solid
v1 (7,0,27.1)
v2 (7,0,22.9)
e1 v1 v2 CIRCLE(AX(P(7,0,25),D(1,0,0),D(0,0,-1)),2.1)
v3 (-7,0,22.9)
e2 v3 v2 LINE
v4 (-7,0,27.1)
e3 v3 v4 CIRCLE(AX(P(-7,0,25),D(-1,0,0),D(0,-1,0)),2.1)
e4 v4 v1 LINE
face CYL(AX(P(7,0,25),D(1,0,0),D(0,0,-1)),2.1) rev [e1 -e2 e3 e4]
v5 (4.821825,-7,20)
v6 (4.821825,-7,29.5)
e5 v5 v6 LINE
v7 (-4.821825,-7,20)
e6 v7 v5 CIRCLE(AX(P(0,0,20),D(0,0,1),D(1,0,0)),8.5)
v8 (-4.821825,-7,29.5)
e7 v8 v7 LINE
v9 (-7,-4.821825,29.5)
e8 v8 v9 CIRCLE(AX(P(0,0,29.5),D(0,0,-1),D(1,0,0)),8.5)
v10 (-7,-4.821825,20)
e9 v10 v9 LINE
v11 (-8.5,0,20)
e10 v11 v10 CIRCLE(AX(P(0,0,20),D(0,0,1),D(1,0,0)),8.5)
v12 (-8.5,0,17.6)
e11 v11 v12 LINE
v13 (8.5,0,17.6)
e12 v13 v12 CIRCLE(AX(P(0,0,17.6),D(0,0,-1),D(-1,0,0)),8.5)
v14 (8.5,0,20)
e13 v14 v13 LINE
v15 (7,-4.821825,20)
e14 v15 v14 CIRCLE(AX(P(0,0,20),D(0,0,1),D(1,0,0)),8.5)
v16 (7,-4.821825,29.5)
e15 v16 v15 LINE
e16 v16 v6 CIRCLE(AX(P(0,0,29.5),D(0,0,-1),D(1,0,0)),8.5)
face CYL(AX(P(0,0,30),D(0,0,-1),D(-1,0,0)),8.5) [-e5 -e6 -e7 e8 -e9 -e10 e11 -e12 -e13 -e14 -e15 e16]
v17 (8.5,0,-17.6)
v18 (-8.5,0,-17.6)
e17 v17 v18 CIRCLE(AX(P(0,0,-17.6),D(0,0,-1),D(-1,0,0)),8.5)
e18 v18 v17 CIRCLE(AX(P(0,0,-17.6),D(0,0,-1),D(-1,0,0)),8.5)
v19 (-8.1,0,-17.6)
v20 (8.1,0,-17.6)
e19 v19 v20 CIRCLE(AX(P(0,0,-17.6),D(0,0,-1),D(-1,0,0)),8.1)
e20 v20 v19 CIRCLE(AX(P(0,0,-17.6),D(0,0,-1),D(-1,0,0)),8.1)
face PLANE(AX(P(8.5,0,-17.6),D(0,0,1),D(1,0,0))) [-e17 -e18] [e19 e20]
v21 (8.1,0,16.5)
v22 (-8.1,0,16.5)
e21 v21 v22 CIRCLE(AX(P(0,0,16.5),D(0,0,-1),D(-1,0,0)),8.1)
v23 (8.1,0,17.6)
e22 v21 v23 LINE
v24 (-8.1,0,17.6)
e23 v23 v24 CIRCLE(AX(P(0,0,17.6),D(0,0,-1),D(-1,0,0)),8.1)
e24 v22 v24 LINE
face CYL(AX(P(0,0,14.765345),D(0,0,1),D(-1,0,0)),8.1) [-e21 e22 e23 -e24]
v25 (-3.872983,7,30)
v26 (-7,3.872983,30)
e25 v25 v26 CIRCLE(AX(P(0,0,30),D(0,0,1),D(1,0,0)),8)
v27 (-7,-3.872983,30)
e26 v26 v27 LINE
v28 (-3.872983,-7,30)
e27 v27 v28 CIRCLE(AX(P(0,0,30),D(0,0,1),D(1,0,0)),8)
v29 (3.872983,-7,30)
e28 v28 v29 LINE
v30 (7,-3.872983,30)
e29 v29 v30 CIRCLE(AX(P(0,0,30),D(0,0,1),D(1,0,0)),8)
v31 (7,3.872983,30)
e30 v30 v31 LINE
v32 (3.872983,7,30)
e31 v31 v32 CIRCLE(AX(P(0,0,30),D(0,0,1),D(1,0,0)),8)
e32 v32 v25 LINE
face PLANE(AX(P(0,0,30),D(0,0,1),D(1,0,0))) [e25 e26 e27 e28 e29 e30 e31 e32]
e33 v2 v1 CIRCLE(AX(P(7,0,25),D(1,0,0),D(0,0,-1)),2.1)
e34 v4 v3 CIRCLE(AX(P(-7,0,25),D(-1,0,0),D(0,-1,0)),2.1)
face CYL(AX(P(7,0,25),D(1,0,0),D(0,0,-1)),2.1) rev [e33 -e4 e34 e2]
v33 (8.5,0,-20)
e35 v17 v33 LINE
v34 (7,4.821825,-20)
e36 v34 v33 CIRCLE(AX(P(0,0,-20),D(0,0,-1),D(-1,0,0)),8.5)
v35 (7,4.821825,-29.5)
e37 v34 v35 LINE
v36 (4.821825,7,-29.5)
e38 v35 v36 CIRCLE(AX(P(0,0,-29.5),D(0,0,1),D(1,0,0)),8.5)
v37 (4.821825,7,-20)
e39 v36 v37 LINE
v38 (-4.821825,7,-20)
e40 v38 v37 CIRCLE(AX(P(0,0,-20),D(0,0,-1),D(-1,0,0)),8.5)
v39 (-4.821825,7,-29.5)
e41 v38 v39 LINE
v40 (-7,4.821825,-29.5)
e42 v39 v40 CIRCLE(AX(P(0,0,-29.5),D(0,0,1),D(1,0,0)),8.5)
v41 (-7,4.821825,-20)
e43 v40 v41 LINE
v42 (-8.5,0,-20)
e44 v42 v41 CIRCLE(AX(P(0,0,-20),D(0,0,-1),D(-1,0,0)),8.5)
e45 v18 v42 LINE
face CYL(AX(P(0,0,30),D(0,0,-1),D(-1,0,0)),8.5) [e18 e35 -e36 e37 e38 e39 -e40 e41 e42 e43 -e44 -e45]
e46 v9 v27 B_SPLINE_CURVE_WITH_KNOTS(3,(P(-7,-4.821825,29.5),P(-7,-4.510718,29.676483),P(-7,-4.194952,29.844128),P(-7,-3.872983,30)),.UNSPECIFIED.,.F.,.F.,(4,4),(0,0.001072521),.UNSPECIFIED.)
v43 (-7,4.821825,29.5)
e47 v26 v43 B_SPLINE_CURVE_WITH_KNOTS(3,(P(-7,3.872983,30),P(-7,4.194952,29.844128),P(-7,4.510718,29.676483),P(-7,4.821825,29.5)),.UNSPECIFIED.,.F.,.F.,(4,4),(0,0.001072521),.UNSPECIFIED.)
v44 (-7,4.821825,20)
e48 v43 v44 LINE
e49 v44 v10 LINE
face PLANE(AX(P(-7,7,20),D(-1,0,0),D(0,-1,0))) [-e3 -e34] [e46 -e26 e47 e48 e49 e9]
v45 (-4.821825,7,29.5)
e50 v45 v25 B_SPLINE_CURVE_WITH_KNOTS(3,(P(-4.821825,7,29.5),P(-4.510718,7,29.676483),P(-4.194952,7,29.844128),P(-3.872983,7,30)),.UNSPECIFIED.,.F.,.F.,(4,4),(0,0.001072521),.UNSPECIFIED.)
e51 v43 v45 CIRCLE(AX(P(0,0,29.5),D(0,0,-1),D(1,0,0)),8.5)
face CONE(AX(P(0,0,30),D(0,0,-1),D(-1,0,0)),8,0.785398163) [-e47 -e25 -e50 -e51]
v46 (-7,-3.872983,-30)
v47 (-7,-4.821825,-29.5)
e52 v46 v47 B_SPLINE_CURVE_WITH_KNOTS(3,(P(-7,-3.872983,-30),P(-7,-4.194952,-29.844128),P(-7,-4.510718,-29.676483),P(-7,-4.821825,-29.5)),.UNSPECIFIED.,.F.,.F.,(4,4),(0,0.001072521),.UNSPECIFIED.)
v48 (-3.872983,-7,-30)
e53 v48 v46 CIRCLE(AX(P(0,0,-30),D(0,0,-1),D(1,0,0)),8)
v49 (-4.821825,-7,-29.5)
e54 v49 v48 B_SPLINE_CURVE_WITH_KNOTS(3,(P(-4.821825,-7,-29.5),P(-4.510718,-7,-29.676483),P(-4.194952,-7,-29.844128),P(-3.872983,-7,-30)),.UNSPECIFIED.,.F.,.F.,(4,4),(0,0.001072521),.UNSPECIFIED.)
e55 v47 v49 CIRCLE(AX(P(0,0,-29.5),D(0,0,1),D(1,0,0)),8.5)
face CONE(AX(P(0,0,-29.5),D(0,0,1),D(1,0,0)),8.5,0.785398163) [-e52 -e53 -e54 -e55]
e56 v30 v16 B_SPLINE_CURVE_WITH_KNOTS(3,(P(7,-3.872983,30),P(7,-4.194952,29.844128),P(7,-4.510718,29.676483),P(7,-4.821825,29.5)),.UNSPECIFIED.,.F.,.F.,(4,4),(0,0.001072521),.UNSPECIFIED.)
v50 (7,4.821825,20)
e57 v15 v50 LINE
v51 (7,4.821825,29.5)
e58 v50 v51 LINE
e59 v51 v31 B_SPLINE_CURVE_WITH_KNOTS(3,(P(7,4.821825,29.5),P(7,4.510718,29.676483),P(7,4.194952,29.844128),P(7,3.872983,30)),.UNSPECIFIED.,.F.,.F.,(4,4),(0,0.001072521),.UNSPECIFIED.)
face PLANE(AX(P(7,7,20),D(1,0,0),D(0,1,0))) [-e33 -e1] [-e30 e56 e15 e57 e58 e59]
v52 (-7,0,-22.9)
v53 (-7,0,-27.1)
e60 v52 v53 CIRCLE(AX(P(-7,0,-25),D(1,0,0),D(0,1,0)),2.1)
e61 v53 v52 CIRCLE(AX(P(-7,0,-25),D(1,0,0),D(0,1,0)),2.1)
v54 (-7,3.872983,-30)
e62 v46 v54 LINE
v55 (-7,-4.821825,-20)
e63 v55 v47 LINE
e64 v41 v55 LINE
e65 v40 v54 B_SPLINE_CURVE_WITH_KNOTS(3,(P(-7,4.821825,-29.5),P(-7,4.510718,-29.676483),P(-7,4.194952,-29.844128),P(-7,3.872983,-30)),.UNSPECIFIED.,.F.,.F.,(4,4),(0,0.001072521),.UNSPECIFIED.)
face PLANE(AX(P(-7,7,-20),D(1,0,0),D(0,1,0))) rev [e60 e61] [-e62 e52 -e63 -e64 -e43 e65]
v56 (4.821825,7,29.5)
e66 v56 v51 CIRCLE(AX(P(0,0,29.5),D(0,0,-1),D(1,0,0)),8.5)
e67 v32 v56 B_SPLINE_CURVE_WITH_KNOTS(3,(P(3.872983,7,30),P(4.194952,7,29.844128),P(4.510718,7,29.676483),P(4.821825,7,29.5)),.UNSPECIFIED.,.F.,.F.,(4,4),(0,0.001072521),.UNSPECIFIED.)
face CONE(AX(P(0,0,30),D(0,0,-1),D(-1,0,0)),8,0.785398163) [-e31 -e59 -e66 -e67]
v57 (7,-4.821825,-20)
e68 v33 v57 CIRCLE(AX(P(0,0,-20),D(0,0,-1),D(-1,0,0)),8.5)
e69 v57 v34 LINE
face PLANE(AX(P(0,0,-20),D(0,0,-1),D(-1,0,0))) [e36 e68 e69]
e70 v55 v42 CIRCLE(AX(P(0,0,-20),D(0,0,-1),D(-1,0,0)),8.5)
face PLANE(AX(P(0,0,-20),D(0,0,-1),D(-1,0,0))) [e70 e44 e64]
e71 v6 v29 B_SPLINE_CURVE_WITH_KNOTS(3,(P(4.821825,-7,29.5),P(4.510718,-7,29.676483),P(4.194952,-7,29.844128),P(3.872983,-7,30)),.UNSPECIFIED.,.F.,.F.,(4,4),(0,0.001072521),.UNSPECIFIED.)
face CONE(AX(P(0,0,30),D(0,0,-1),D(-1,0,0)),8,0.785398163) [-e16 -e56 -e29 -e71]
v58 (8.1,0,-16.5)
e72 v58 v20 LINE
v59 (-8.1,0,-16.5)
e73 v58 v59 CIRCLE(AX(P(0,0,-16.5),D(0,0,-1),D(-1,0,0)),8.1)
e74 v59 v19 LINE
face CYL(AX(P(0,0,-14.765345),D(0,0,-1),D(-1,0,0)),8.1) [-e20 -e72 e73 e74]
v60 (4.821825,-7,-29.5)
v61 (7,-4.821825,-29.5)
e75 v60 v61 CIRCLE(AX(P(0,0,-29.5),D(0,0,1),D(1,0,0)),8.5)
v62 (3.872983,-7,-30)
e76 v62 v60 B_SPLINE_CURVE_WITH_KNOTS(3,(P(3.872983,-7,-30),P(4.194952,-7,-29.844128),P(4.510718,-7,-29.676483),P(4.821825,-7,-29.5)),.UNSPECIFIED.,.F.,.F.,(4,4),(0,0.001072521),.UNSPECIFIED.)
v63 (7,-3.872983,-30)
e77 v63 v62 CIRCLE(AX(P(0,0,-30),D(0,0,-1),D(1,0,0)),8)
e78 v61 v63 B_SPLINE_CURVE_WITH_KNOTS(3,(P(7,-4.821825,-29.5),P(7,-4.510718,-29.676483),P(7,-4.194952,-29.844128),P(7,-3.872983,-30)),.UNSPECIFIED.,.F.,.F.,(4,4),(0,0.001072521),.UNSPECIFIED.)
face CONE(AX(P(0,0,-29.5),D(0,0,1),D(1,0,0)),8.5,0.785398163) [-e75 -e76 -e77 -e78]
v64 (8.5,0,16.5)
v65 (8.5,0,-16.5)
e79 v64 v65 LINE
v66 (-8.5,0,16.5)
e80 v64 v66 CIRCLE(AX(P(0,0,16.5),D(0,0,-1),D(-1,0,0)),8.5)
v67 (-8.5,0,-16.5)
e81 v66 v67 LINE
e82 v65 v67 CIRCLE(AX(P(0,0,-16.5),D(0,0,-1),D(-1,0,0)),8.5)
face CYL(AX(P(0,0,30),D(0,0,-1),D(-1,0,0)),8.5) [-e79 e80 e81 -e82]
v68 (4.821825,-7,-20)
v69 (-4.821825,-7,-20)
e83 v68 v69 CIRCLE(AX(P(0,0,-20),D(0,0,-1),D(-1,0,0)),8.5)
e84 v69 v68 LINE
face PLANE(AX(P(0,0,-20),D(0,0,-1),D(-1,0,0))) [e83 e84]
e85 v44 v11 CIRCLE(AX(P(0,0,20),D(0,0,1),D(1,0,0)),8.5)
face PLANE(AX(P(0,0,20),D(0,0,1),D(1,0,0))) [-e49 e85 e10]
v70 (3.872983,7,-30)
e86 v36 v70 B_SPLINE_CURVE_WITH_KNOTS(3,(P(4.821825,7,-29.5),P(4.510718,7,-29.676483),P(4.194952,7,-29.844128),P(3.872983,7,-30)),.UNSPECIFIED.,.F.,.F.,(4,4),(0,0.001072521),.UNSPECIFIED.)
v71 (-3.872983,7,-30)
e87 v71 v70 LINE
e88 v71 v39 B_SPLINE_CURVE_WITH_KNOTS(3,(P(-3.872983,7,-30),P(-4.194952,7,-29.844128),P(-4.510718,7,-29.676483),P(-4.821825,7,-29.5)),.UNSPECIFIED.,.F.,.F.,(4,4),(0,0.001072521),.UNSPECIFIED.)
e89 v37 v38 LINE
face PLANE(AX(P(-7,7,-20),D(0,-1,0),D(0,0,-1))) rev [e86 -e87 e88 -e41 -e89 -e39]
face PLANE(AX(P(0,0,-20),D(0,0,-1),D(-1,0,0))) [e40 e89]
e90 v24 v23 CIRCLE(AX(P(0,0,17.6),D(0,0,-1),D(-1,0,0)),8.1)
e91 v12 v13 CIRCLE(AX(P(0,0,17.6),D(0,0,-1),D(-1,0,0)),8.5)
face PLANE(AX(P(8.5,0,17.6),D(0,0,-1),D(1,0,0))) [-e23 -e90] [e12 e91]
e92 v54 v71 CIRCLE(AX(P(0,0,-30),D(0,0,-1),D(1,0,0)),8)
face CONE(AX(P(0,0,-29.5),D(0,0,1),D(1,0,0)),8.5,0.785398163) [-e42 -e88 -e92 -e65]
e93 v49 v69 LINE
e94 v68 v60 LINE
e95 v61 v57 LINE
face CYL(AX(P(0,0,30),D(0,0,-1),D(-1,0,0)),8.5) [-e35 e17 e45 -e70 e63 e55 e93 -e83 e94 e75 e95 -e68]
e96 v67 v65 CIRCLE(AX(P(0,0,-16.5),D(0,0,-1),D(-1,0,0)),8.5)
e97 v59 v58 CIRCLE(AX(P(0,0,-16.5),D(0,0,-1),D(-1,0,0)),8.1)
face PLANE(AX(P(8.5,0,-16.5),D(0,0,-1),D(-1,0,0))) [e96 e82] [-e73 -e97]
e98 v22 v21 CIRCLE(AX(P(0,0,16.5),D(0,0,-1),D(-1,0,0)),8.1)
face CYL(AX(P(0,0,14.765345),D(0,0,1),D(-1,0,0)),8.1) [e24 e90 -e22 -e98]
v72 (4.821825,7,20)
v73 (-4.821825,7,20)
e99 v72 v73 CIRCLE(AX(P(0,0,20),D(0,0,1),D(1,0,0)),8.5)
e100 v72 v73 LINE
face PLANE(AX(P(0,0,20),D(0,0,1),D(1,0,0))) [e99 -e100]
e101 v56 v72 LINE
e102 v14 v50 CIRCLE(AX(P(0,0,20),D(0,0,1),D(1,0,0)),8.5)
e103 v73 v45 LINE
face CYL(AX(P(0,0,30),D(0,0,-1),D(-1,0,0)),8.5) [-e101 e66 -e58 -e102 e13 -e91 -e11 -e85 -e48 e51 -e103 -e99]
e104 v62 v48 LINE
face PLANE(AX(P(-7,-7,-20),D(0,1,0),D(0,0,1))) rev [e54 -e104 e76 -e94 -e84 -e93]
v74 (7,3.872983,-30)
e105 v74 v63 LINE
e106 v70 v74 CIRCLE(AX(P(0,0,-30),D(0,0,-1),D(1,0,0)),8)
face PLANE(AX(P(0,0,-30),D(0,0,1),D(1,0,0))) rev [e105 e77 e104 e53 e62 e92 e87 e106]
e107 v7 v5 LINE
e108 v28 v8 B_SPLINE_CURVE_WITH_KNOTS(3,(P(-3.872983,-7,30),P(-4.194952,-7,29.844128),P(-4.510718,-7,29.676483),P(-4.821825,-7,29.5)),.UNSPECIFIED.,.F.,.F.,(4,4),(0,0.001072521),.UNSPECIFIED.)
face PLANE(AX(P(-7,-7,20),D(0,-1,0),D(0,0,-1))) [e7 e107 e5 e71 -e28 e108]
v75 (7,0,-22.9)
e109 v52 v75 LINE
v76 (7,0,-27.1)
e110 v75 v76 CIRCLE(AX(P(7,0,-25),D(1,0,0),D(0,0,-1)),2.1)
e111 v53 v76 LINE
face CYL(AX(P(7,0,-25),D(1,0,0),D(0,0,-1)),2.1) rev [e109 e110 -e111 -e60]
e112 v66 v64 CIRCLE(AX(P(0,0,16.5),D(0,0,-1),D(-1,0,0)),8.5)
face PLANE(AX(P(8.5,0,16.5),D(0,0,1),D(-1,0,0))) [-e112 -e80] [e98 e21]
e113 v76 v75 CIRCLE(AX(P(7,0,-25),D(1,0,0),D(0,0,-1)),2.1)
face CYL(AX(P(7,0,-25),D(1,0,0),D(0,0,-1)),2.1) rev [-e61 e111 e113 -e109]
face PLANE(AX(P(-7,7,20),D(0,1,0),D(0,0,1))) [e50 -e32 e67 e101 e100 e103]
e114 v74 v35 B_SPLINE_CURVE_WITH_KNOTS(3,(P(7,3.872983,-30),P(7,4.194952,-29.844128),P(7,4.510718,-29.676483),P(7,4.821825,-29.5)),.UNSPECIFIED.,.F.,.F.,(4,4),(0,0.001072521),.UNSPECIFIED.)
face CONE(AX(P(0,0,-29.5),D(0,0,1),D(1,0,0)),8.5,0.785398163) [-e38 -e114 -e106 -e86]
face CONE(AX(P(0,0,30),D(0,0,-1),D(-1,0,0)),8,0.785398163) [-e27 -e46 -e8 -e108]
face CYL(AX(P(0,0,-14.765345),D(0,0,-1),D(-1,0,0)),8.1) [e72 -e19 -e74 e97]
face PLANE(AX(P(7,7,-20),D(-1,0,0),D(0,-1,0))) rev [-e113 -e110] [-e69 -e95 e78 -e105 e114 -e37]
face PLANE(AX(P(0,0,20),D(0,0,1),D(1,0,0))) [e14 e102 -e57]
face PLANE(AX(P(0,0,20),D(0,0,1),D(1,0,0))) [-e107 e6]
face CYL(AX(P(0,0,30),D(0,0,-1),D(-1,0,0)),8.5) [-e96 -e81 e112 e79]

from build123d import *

# Parameters (mm, degrees)
SKETCH_1_R           = 8.5
EXTRUDE_1_DEPTH      = 30
SKETCH_4_OUTSIDE_W   = 31.928
SKETCH_4_OUTSIDE_H   = 31.928
SKETCH_4_OUTSIDE_W_2 = 14
SKETCH_4_OUTSIDE_H_2 = 14
CUT_EXTRUDE_1_DEPTH  = 10
HOLE_WIZARD_M5_1_D   = 4.2
CHAMFER_1_SIZE       = 0.5
SKETCH_7_W           = 0.4
SKETCH_7_H           = 1.1


with BuildPart() as part:
    # 草图1 → 凸台-拉伸1 (new, symmetric)
    with BuildSketch(Plane.XY):
        Circle(SKETCH_1_R)
    extrude(amount=EXTRUDE_1_DEPTH, both=True)

    # 草图4 outside → 切除-拉伸1 (cut)
    with BuildSketch(Plane.XY.offset(30)):
        Rectangle(SKETCH_4_OUTSIDE_W, SKETCH_4_OUTSIDE_H)
        Rectangle(SKETCH_4_OUTSIDE_W_2, SKETCH_4_OUTSIDE_H_2, mode=Mode.SUBTRACT)
    cut_extrude_1 = extrude(amount=-CUT_EXTRUDE_1_DEPTH, mode=Mode.SUBTRACT)

    # M5 螺纹孔1 (through all)
    with Locations(Plane(origin=(7, 0, 0), x_dir=(0, 0, -1), z_dir=(1, 0, 0))):
        with Locations((-25, 0)):
            hole_wizard_m5_1 = Hole(HOLE_WIZARD_M5_1_D / 2)

    # 镜向1: 切除-拉伸1, M5 螺纹孔1 across plane
    add(cut_extrude_1.mirror(Plane.XY), mode=Mode.SUBTRACT)
    add(hole_wizard_m5_1.mirror(Plane.XY), mode=Mode.SUBTRACT)

    # 倒角1
    chamfer_1_edges = [part.edges().sort_by_distance(p)[0] for p in [
        (6.01040764, 6.01040764, -30),
        (6.01040764, 6.01040764, 30),
        (-6.01040764, 6.01040764, 30),
        (-6.01040764, 6.01040764, -30),
        (-6.01040764, -6.01040764, -30),
        (6.01040764, -6.01040764, -30),
        (-6.01040764, -6.01040764, 30),
        (6.01040764, -6.01040764, 30),
    ]]
    chamfer(chamfer_1_edges, length=CHAMFER_1_SIZE)

    # 草图7 → 切除-旋转1 (revolve, cut)
    with BuildSketch(Plane(origin=(0, 0, 0), x_dir=(1, 0, 0), z_dir=(0, 1, 0)), mode=Mode.PRIVATE) as cut_revolve_1_sk:
        with Locations((8.3, 17.05)):
            Rectangle(SKETCH_7_W, SKETCH_7_H)
    cut_revolve_1 = revolve(cut_revolve_1_sk.sketch.rotate(Axis((0, 0, -14.7653446), (0, 0, 1)), 180), axis=Axis((0, 0, -14.7653446), (0, 0, 1)), mode=Mode.SUBTRACT)

    # 镜向2: 切除-旋转1 across plane
    add(cut_revolve_1.mirror(Plane.XY), mode=Mode.SUBTRACT)


solid = part.part
